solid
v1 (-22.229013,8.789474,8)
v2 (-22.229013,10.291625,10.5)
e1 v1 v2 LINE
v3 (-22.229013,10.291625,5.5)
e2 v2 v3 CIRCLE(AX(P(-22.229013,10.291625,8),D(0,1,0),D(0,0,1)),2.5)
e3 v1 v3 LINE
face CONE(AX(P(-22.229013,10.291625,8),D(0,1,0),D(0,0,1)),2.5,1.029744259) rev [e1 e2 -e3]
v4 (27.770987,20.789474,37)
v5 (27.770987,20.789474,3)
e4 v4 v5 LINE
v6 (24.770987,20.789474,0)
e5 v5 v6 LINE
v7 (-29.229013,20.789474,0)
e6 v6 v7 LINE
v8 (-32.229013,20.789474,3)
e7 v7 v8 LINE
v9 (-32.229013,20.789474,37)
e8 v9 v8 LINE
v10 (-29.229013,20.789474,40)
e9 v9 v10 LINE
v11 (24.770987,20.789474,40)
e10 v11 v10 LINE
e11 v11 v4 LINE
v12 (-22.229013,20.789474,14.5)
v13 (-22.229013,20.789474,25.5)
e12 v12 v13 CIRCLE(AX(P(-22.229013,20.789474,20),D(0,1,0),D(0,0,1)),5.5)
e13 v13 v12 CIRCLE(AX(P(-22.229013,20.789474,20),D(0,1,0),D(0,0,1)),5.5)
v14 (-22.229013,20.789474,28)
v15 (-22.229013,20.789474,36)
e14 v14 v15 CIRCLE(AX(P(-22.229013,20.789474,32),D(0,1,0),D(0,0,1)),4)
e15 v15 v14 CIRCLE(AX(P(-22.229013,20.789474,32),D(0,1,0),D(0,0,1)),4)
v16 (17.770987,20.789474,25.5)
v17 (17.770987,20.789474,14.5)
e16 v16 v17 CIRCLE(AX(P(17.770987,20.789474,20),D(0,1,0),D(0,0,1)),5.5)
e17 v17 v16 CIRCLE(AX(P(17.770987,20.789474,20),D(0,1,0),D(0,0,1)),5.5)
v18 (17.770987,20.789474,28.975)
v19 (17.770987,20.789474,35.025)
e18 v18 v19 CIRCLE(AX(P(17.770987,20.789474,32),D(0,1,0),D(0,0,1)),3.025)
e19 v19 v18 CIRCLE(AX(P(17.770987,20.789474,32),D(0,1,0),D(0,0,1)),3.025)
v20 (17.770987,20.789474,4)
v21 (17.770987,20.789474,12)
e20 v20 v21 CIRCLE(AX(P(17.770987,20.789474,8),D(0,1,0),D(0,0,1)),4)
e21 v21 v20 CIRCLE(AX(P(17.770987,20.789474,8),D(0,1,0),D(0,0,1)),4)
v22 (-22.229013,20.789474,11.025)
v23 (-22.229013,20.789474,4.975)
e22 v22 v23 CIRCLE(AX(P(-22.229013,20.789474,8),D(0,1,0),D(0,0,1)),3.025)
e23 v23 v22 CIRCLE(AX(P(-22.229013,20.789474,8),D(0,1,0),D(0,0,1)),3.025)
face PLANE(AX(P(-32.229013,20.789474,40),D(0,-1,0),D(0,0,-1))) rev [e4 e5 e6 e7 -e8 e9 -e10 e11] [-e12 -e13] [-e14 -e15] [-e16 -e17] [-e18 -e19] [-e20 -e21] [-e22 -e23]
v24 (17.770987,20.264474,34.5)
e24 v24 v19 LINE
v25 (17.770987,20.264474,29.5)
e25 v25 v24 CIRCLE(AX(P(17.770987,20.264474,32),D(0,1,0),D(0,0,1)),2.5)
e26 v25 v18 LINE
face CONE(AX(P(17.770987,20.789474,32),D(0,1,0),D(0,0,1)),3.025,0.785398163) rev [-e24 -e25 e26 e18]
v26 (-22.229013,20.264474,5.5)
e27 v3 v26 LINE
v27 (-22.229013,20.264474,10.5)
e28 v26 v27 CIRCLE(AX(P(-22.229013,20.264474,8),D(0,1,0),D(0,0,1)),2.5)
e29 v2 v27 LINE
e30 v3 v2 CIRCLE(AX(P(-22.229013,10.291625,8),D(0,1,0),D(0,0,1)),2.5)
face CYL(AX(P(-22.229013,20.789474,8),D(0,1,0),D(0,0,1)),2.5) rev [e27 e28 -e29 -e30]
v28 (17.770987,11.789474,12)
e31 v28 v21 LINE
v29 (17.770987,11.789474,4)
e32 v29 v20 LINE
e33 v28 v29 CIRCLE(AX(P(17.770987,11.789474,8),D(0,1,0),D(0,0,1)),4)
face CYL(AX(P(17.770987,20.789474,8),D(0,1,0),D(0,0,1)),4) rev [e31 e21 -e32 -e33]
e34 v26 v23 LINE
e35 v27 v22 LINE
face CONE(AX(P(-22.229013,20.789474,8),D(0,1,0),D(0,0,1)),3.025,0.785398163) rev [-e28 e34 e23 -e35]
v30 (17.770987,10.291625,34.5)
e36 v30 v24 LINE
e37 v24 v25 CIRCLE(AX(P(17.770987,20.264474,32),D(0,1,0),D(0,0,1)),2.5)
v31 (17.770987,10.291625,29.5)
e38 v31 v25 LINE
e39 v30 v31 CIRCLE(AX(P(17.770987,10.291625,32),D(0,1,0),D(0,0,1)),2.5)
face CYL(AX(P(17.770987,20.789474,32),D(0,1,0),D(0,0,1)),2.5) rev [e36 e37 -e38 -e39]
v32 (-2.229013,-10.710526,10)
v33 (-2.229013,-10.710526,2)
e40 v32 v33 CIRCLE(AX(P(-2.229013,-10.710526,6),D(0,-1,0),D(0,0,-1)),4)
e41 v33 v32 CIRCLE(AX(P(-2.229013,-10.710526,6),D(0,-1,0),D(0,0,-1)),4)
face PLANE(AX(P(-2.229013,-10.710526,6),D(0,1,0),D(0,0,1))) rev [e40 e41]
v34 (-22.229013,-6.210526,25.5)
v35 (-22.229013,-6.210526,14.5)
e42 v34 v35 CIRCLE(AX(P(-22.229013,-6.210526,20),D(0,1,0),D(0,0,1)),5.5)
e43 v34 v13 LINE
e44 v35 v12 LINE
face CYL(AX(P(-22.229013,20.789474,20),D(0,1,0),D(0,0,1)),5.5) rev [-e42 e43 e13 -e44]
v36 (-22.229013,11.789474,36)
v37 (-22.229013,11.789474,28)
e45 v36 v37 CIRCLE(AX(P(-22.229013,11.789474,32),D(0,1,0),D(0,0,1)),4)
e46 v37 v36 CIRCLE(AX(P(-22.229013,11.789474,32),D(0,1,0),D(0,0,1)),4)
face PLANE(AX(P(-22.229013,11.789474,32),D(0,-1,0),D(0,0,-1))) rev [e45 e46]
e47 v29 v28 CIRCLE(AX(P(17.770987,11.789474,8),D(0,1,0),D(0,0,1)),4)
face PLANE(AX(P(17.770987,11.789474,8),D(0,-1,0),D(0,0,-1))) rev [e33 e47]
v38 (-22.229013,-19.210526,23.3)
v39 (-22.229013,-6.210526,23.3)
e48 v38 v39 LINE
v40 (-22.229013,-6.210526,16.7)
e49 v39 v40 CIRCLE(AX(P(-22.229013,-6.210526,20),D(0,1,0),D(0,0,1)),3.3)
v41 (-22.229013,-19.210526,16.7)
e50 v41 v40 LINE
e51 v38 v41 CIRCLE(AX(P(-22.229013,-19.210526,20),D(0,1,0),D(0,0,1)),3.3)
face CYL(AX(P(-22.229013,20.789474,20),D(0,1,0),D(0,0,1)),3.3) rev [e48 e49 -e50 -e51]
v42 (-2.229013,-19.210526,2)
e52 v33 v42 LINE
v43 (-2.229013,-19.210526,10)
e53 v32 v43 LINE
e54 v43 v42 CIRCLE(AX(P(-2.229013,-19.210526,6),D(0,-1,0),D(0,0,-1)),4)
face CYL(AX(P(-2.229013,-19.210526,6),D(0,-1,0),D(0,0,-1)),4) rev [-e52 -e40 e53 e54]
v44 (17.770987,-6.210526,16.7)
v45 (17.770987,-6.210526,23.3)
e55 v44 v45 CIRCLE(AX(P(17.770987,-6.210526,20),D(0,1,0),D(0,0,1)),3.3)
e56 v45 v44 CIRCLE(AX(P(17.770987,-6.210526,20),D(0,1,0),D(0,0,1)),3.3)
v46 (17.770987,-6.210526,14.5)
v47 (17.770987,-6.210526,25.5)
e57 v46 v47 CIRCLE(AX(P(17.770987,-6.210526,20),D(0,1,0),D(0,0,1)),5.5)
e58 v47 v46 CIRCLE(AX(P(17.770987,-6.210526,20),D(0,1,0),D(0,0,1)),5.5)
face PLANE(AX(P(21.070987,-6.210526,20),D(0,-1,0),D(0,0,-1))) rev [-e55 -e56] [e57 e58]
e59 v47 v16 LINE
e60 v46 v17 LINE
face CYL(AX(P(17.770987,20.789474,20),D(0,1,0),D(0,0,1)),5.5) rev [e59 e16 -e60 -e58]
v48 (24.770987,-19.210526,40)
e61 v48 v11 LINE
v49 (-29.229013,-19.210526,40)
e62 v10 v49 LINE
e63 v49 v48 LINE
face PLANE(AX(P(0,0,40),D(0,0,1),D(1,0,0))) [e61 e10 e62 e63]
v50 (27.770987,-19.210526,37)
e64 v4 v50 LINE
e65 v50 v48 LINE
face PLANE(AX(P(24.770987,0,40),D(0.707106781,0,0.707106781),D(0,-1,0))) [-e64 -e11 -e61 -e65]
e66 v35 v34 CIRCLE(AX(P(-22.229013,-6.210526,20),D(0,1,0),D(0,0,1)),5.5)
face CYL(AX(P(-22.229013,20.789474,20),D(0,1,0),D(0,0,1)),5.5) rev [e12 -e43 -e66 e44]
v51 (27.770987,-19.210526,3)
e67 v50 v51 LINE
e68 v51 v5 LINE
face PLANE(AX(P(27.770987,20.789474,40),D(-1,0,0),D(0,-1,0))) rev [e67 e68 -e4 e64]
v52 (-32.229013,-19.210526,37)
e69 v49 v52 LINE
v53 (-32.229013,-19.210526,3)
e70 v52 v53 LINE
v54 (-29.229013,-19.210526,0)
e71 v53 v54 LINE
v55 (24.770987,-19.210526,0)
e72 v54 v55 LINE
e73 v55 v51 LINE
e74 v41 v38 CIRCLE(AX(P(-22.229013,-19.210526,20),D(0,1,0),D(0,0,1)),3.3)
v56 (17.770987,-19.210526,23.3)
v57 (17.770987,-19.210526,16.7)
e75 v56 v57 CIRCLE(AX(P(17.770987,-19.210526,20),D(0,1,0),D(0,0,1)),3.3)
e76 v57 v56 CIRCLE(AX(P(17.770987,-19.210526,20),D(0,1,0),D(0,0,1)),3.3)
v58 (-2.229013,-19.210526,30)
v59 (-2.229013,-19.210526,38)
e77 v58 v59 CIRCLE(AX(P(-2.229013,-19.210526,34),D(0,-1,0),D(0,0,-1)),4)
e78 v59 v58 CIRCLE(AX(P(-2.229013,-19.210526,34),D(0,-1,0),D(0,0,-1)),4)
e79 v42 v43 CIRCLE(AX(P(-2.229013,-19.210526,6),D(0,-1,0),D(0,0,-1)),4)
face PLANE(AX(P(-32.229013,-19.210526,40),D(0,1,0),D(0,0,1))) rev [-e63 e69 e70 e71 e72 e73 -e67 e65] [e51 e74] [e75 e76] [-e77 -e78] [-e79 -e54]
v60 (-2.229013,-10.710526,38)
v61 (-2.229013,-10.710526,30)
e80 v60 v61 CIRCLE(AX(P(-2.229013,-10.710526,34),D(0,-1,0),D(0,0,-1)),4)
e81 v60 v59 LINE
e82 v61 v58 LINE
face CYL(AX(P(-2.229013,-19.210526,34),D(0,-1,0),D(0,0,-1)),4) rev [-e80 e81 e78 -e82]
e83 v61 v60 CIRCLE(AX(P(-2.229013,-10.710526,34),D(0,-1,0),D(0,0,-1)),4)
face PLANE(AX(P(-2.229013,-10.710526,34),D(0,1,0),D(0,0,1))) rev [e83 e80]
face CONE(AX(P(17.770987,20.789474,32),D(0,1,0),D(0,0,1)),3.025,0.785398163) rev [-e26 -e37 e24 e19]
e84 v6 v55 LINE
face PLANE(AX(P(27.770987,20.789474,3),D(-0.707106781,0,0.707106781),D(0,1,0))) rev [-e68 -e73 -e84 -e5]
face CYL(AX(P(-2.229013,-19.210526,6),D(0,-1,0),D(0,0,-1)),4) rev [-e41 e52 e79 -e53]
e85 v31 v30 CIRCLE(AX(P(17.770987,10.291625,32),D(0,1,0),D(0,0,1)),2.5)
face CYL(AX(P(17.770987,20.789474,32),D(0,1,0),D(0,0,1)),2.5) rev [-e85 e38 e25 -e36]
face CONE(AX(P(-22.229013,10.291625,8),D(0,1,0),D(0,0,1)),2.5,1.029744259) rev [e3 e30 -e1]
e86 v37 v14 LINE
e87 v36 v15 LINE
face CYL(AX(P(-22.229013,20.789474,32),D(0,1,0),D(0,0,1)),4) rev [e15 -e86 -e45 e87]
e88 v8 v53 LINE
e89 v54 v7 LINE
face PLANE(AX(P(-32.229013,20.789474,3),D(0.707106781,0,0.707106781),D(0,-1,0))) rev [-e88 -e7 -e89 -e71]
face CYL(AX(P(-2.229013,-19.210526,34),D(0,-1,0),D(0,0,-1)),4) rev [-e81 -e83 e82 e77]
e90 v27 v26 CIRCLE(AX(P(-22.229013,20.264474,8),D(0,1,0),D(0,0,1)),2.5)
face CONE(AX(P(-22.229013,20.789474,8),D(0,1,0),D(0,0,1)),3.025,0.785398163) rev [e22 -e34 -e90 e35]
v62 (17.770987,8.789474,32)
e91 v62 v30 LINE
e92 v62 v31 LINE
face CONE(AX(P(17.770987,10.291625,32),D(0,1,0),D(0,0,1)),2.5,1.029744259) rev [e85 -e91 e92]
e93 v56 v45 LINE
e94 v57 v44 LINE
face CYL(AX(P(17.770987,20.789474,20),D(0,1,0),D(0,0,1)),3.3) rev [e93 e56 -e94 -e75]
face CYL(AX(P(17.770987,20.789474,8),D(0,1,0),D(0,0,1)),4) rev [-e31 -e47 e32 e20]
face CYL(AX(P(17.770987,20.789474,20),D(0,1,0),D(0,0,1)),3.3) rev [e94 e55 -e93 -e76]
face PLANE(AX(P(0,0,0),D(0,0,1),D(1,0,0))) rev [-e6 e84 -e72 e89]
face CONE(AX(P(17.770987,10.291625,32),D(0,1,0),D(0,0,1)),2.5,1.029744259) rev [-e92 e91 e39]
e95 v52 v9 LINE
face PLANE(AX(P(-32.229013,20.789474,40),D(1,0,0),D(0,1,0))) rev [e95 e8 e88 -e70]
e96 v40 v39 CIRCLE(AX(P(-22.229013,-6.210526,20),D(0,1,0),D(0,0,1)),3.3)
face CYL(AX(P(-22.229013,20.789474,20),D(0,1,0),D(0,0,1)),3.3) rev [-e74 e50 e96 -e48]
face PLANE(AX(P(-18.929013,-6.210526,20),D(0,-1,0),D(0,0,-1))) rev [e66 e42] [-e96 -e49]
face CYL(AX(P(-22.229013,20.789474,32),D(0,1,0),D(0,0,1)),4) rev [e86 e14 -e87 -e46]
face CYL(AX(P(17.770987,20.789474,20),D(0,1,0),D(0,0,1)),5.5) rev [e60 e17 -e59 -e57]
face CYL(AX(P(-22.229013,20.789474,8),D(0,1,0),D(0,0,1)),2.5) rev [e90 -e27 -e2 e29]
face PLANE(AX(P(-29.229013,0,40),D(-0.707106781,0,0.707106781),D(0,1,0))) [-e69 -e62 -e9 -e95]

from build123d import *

# Parameters (mm, degrees)
SKETCH1_W                   = 60
SKETCH1_H                   = 40
BOSS_EXTRUDE1_DEPTH         = 40
CHAMFER1_SIZE               = 3
M6_TAPPED_HOLE1_D           = 5
M6_TAPPED_HOLE1_DEPTH       = 10.497848452
M6_TAPPED_HOLE1_CSINK_D     = 6.05
M6_TAPPED_HOLE1_CSINK_ANGLE = 90
M6_TAPPED_HOLE1_TIP         = 1.502151548
HOLE1_D                     = 6.6
HOLE1_CBORE_D               = 11
HOLE1_CBORE_DEPTH           = 27
HOLE2_D                     = 8
HOLE2_DEPTH                 = 9
HOLE3_D                     = 8
HOLE3_DEPTH                 = 8.5


with BuildPart() as part:
    # Sketch1 → Boss-Extrude1 (new body)
    with BuildSketch(Plane.XY):
        with Locations((-2.229013427, 0.789473684)):
            Rectangle(SKETCH1_W, SKETCH1_H)
    extrude(amount=BOSS_EXTRUDE1_DEPTH)

    # Chamfer1
    chamfer1_edges = [part.edges().sort_by_distance(p)[0] for p in [
        (27.770986573, 0.789473684, 40),
        (-32.229013427, 0.789473684, 40),
        (27.770986573, 0.789473684, 0),
        (-32.229013427, 0.789473684, 0),
    ]]
    chamfer(chamfer1_edges, length=CHAMFER1_SIZE)

    # M6 Tapped Hole1
    with Locations(Plane(origin=(0, 20.789473684, 0), x_dir=(1, 0, 0), z_dir=(0, 1, 0))):
        with Locations((-22.229013427, -8), (17.770986573, -32)):
            CounterSinkHole(M6_TAPPED_HOLE1_D / 2, M6_TAPPED_HOLE1_CSINK_D / 2, depth=M6_TAPPED_HOLE1_DEPTH, counter_sink_angle=M6_TAPPED_HOLE1_CSINK_ANGLE)
            with Locations((0, 0, -(M6_TAPPED_HOLE1_DEPTH + M6_TAPPED_HOLE1_TIP / 2))):  # 118° drill point
                Cone(0, M6_TAPPED_HOLE1_D / 2, M6_TAPPED_HOLE1_TIP, mode=Mode.SUBTRACT)

    # Hole1 (through all)
    with Locations(Plane(origin=(0, 20.789473684, 0), x_dir=(1, 0, 0), z_dir=(0, 1, 0))):
        with Locations((-22.229013427, -20), (17.770986573, -20)):
            CounterBoreHole(HOLE1_D / 2, HOLE1_CBORE_D / 2, HOLE1_CBORE_DEPTH)

    # Hole2
    with Locations(Plane(origin=(0, 20.789473684, 0), x_dir=(1, 0, 0), z_dir=(0, 1, 0))):
        with Locations((17.770986573, -8), (-22.229013427, -32)):
            Hole(HOLE2_D / 2, depth=HOLE2_DEPTH)

    # Hole3
    with Locations(Plane(origin=(0, -19.210526316, 0), x_dir=(-1, 0, 0), z_dir=(0, -1, 0))):
        with Locations((2.229013427, -34), (2.229013427, -6)):
            Hole(HOLE3_D / 2, depth=HOLE3_DEPTH)


solid = part.part
